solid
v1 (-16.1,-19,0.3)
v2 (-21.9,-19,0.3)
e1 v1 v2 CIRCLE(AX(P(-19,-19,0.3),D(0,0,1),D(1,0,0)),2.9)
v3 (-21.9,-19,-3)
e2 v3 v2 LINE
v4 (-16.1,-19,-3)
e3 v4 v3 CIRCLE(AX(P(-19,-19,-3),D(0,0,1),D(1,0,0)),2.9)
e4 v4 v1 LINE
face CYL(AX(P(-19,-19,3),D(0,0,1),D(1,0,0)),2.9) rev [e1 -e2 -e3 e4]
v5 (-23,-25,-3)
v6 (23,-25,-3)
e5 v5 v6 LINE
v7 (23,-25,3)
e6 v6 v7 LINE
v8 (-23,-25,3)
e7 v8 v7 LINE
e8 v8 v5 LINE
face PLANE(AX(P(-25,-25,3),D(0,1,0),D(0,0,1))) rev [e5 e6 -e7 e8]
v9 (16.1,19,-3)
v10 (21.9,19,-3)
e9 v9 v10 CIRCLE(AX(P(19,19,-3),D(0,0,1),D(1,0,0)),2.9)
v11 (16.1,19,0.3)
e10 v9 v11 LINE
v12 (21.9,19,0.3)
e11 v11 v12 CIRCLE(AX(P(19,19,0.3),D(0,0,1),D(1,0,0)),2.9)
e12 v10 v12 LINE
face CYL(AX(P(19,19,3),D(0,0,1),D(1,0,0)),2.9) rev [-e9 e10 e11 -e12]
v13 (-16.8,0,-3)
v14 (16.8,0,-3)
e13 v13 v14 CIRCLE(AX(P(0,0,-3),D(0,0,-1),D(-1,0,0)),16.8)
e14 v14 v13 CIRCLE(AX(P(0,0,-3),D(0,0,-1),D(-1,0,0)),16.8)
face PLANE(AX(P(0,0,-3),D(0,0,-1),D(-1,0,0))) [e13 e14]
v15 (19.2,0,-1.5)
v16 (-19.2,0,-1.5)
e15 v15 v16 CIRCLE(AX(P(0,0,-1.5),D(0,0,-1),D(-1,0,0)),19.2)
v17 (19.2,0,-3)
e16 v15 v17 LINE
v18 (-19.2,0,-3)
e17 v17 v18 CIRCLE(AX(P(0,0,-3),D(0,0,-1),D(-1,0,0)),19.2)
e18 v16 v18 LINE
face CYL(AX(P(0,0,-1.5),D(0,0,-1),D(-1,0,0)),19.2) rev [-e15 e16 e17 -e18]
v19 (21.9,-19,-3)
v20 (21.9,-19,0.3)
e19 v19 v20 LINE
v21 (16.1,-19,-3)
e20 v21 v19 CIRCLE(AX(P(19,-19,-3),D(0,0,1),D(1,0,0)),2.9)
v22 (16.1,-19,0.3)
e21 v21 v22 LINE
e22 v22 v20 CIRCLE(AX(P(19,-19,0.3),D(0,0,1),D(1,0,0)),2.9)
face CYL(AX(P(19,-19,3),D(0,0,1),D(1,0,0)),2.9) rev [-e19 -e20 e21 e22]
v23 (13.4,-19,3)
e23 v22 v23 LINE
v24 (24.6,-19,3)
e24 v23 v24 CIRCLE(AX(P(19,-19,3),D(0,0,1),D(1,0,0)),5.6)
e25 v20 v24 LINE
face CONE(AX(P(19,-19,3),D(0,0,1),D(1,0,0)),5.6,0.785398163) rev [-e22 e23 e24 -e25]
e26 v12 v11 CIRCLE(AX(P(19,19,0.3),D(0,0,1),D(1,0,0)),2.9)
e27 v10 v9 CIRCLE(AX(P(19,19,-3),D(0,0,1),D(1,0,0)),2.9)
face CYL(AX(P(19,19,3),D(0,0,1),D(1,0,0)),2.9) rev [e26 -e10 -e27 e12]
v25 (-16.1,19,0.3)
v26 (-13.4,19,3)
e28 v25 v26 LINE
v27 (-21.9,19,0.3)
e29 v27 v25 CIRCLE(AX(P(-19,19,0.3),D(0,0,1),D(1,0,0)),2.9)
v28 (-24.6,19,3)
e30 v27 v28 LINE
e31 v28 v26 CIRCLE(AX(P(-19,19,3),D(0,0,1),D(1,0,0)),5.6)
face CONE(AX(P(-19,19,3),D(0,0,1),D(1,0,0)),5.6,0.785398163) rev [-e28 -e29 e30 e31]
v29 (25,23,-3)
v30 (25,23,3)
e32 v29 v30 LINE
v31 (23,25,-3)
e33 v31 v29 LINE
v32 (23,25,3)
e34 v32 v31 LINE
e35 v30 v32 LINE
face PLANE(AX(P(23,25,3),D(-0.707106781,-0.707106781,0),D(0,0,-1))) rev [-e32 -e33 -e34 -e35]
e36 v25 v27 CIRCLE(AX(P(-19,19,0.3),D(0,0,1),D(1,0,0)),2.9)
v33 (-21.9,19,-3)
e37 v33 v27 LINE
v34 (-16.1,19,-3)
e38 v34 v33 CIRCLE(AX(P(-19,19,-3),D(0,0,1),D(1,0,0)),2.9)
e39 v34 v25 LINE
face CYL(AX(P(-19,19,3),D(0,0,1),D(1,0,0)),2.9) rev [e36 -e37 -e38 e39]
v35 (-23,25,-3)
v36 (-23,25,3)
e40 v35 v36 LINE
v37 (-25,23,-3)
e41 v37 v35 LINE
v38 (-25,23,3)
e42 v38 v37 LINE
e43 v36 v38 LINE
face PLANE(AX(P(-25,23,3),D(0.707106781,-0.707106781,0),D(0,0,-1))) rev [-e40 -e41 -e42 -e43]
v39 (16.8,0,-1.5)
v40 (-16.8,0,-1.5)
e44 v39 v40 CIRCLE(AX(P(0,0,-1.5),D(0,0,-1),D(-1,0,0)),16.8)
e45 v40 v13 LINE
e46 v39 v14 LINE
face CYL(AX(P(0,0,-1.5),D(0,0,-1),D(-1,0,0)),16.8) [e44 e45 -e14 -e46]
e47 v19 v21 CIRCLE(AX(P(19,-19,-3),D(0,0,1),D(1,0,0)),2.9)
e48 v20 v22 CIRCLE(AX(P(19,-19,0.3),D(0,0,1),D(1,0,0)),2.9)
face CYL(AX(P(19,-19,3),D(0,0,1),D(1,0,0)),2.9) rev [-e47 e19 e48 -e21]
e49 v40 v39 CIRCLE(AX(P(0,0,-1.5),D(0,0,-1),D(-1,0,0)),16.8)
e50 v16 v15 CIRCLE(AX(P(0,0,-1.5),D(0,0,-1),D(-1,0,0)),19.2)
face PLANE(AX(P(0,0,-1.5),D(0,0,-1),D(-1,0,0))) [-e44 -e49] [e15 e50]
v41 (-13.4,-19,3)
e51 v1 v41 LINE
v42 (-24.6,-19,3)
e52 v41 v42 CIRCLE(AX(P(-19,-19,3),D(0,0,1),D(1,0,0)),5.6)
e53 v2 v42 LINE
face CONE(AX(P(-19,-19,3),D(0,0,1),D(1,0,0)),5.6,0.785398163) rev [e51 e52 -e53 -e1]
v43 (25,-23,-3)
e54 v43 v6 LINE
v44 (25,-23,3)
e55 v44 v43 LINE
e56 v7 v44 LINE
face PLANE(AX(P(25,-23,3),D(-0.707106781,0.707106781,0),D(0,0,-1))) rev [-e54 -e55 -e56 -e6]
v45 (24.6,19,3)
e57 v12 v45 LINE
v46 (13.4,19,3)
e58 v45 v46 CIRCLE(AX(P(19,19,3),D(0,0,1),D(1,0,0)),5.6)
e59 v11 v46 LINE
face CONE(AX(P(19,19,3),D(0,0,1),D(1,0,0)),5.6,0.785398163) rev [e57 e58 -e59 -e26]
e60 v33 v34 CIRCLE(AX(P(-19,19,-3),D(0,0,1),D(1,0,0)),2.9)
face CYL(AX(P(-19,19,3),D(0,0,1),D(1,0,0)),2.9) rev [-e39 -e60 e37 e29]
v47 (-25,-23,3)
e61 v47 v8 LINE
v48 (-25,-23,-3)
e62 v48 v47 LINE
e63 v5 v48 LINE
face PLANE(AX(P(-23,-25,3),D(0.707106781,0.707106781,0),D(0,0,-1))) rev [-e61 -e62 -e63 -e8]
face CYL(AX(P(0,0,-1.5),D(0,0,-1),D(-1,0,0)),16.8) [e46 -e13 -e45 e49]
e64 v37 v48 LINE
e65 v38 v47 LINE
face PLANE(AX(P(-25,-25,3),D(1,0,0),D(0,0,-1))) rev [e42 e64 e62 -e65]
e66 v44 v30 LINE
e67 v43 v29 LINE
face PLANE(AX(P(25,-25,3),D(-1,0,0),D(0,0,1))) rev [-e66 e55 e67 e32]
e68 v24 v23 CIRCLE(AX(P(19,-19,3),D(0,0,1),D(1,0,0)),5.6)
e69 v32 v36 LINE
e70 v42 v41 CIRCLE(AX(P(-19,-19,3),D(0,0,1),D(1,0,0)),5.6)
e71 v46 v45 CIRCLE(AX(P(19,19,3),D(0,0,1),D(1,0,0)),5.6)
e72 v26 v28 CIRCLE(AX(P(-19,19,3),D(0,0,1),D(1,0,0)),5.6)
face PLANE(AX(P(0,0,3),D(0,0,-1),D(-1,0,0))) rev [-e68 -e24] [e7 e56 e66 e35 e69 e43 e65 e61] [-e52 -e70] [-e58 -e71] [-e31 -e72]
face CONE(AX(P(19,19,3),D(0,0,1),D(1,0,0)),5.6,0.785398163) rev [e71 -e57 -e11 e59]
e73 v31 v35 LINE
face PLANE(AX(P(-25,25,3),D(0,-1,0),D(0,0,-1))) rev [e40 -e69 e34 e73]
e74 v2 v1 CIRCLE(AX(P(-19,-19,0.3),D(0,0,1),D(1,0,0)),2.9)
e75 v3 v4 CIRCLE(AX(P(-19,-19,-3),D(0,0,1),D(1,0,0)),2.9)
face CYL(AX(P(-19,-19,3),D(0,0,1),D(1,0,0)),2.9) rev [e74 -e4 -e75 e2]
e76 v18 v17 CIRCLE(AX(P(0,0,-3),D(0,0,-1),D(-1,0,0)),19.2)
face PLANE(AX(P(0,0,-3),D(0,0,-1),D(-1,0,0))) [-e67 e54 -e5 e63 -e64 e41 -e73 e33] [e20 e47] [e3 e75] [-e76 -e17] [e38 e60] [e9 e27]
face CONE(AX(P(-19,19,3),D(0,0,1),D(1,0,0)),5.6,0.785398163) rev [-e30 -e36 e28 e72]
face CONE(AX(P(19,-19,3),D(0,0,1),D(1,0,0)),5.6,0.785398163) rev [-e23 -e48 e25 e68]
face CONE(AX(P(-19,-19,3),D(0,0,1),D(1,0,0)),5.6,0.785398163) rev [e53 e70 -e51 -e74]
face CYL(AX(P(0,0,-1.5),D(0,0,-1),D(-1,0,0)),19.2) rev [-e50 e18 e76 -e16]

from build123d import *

# Parameters (mm, degrees)
SKETCH_1_W                   = 50
SKETCH_1_H                   = 50
EXTRUDE_1_DEPTH              = 3
HOLE_WIZARD_M5_1_D           = 5.8
HOLE_WIZARD_M5_1_CSINK_D     = 11.2
HOLE_WIZARD_M5_1_CSINK_ANGLE = 90
CHAMFER_1_SIZE               = 2
SKETCH_8_R                   = 19.2
SKETCH_8_R_2                 = 16.8
CUT_EXTRUDE_2_DEPTH          = 1.5


with BuildPart() as part:
    # 草图1 → 凸台-拉伸1 (new, symmetric)
    with BuildSketch(Plane.XY):
        Rectangle(SKETCH_1_W, SKETCH_1_H)
    extrude(amount=EXTRUDE_1_DEPTH, both=True)

    # M5 六角凹锥坑螺钉的锥形沉头孔1 (through all)
    with Locations(Plane.XY.offset(3)):
        with Locations((-19, 19), (19, 19), (-19, -19), (19, -19)):
            CounterSinkHole(HOLE_WIZARD_M5_1_D / 2, HOLE_WIZARD_M5_1_CSINK_D / 2, counter_sink_angle=HOLE_WIZARD_M5_1_CSINK_ANGLE)

    # 倒角1
    chamfer_1_edges = [part.edges().sort_by_distance(p)[0] for p in [
        (25, -25, 0),
        (-25, -25, 0),
        (-25, 25, 0),
        (25, 25, 0),
    ]]
    chamfer(chamfer_1_edges, length=CHAMFER_1_SIZE)

    # 草图8 → 切除-拉伸2 (cut)
    with BuildSketch(Plane(origin=(0, 0, -3), x_dir=(-1, 0, 0), z_dir=(0, 0, -1))):
        Circle(SKETCH_8_R)
        Circle(SKETCH_8_R_2, mode=Mode.SUBTRACT)
    extrude(amount=-CUT_EXTRUDE_2_DEPTH, mode=Mode.SUBTRACT)


solid = part.part
